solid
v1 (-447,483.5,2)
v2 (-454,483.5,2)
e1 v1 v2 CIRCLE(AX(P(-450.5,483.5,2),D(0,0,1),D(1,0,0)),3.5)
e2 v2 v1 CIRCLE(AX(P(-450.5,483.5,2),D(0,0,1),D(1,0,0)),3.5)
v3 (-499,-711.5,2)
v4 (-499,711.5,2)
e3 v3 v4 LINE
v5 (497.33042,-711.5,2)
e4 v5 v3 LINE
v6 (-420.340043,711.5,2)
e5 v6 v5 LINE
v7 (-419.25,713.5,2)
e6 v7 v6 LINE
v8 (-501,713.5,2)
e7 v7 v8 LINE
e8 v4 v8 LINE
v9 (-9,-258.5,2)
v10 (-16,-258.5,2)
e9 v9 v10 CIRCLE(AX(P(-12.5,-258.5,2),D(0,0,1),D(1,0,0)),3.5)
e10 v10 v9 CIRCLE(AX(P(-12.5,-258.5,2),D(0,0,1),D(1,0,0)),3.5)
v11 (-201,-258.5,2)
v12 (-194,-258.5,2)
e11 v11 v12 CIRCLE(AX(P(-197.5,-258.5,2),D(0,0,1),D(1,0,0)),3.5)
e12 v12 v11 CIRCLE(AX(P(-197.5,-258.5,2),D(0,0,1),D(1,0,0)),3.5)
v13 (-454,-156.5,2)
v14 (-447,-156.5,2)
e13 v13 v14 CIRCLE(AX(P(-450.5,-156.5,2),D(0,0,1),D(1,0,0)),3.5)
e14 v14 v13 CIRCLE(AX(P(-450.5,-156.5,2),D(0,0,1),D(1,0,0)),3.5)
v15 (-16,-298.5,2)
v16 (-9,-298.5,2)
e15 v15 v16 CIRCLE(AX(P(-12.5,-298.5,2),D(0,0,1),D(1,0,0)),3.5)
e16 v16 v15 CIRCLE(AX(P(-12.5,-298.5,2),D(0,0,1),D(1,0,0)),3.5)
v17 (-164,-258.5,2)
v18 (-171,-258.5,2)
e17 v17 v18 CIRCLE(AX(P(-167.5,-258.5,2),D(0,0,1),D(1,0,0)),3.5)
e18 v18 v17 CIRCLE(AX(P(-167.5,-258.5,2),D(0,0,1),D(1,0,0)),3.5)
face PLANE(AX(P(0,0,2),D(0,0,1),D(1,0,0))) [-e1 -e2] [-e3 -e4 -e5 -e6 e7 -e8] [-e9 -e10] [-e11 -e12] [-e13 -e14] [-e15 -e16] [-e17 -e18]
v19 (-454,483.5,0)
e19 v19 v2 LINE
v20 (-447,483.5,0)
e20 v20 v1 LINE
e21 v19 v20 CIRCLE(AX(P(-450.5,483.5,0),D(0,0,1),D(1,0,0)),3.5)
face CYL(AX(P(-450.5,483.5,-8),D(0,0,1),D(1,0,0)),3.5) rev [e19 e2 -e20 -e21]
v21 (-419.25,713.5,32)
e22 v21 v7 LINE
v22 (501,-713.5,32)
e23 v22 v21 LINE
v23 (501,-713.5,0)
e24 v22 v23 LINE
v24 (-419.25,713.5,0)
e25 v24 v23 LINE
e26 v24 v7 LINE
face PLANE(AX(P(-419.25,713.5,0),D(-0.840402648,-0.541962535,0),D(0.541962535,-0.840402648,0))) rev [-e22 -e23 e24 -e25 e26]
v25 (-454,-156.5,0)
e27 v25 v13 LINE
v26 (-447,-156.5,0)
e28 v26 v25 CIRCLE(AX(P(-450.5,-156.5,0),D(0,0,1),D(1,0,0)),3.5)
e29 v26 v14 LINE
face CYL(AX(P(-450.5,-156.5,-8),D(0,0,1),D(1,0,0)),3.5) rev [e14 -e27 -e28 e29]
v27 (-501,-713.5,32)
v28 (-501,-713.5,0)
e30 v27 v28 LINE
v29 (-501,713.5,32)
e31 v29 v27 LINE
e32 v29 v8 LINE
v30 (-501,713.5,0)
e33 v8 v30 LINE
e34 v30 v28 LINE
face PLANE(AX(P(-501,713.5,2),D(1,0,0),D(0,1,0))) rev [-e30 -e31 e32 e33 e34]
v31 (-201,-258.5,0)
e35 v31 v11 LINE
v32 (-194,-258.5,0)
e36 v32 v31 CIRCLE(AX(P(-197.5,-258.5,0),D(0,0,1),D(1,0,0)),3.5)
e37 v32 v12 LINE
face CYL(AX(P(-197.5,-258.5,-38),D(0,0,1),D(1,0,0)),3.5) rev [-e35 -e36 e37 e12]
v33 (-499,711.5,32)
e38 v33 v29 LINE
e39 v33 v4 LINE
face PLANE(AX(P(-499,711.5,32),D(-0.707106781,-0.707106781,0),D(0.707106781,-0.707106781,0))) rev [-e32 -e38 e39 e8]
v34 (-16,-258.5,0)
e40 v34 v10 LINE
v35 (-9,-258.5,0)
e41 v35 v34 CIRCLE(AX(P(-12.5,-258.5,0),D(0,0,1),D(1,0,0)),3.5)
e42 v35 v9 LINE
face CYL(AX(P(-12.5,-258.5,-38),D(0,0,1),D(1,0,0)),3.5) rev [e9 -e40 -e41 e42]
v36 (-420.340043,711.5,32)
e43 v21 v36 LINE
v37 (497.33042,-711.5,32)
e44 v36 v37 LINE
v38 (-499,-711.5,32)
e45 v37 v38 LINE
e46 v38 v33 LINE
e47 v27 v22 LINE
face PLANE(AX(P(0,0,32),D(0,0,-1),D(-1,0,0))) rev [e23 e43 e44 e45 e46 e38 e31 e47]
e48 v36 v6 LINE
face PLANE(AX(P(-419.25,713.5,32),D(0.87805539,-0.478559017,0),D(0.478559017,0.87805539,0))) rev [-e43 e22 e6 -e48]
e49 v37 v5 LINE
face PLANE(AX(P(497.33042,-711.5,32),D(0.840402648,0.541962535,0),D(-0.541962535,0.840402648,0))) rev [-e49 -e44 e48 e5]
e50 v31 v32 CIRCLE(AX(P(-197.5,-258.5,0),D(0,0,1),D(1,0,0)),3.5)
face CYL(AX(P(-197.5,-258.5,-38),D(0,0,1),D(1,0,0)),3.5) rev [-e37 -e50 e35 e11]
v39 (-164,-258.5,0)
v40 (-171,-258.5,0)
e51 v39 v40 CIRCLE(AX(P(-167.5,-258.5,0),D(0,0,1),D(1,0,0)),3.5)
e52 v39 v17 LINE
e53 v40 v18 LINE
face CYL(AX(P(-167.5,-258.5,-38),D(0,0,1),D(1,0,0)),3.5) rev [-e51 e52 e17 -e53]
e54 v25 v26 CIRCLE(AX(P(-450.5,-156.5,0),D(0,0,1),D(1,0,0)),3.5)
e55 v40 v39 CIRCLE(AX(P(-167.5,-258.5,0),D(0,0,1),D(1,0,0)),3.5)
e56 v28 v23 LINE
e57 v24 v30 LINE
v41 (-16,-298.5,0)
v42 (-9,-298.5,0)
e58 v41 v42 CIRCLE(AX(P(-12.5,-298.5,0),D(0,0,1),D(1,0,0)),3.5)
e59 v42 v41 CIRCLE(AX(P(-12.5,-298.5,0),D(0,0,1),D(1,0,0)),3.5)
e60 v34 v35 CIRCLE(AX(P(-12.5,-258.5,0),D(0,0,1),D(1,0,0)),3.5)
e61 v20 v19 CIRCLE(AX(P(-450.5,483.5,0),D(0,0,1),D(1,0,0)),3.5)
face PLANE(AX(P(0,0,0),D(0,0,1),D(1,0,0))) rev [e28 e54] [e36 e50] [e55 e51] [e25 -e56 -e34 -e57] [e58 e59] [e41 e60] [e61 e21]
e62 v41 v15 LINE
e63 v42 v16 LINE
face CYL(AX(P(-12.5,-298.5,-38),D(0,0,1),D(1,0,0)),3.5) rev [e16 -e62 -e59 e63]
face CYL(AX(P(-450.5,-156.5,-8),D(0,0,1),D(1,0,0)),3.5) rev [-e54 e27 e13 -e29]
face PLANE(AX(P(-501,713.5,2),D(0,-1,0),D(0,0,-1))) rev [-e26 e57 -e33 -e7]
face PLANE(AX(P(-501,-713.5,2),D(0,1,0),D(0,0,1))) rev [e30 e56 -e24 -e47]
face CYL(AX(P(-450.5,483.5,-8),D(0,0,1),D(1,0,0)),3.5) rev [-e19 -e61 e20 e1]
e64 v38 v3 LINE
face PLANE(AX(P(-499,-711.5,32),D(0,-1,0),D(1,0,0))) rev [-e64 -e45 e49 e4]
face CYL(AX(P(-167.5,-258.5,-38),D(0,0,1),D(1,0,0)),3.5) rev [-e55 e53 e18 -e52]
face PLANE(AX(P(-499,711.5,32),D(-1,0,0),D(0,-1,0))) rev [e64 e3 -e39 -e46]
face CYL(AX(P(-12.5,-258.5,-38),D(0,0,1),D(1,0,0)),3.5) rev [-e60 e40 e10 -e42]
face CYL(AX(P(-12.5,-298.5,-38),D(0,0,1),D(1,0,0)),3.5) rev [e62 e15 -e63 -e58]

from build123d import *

# Parameters (mm, degrees)
SKETCH1_W           = 1002
SKETCH1_H           = 1427
BOSS_EXTRUDE1_DEPTH = 2
CUT_EXTRUDE1_DEPTH  = 2
SKETCH5_R           = 3.5
CUT_EXTRUDE2_DEPTH  = 40
BOSS_EXTRUDE2_DEPTH = 30
SKETCH7_R           = 3.5
CUT_EXTRUDE3_DEPTH  = 10


with BuildPart() as part:
    # Sketch1 → Boss-Extrude1 (new body)
    with BuildSketch(Plane.XY):
        Rectangle(SKETCH1_W, SKETCH1_H)
    extrude(amount=BOSS_EXTRUDE1_DEPTH)

    # Sketch2 → Cut-Extrude1 (cut)
    with BuildSketch(Plane.XY.offset(2)):
        Polygon((-419.25, 713.5), (501, -713.5), (501, 713.5), align=None)
    extrude(amount=-CUT_EXTRUDE1_DEPTH, mode=Mode.SUBTRACT)

    # Sketch5 → Cut-Extrude2 (cut)
    with BuildSketch(Plane.XY.offset(2)):
        with Locations((-197.5, -258.5)):
            Circle(SKETCH5_R)
        with Locations((-167.5, -258.5)):
            Circle(SKETCH5_R)
        with Locations((-12.5, -258.5)):
            Circle(SKETCH5_R)
        with Locations((-12.5, -298.5)):
            Circle(SKETCH5_R)
    extrude(amount=-CUT_EXTRUDE2_DEPTH, mode=Mode.SUBTRACT)

    # Sketch6 → Boss-Extrude2 (add)
    with BuildSketch(Plane.XY.offset(2)):
        Polygon((-499, 711.5), (-499, -711.5), (497.33041962, -711.5), (-420.340042889, 711.5), (-419.25, 713.5), (501, -713.5), (-501, -713.5), (-501, 713.5), align=None)
    extrude(amount=BOSS_EXTRUDE2_DEPTH)

    # Sketch7 → Cut-Extrude3 (cut)
    with BuildSketch(Plane.XY.offset(2)):
        with Locations((-450.5, 483.5)):
            Circle(SKETCH7_R)
        with Locations((-450.5, -156.5)):
            Circle(SKETCH7_R)
    extrude(amount=-CUT_EXTRUDE3_DEPTH, mode=Mode.SUBTRACT)


solid = part.part
